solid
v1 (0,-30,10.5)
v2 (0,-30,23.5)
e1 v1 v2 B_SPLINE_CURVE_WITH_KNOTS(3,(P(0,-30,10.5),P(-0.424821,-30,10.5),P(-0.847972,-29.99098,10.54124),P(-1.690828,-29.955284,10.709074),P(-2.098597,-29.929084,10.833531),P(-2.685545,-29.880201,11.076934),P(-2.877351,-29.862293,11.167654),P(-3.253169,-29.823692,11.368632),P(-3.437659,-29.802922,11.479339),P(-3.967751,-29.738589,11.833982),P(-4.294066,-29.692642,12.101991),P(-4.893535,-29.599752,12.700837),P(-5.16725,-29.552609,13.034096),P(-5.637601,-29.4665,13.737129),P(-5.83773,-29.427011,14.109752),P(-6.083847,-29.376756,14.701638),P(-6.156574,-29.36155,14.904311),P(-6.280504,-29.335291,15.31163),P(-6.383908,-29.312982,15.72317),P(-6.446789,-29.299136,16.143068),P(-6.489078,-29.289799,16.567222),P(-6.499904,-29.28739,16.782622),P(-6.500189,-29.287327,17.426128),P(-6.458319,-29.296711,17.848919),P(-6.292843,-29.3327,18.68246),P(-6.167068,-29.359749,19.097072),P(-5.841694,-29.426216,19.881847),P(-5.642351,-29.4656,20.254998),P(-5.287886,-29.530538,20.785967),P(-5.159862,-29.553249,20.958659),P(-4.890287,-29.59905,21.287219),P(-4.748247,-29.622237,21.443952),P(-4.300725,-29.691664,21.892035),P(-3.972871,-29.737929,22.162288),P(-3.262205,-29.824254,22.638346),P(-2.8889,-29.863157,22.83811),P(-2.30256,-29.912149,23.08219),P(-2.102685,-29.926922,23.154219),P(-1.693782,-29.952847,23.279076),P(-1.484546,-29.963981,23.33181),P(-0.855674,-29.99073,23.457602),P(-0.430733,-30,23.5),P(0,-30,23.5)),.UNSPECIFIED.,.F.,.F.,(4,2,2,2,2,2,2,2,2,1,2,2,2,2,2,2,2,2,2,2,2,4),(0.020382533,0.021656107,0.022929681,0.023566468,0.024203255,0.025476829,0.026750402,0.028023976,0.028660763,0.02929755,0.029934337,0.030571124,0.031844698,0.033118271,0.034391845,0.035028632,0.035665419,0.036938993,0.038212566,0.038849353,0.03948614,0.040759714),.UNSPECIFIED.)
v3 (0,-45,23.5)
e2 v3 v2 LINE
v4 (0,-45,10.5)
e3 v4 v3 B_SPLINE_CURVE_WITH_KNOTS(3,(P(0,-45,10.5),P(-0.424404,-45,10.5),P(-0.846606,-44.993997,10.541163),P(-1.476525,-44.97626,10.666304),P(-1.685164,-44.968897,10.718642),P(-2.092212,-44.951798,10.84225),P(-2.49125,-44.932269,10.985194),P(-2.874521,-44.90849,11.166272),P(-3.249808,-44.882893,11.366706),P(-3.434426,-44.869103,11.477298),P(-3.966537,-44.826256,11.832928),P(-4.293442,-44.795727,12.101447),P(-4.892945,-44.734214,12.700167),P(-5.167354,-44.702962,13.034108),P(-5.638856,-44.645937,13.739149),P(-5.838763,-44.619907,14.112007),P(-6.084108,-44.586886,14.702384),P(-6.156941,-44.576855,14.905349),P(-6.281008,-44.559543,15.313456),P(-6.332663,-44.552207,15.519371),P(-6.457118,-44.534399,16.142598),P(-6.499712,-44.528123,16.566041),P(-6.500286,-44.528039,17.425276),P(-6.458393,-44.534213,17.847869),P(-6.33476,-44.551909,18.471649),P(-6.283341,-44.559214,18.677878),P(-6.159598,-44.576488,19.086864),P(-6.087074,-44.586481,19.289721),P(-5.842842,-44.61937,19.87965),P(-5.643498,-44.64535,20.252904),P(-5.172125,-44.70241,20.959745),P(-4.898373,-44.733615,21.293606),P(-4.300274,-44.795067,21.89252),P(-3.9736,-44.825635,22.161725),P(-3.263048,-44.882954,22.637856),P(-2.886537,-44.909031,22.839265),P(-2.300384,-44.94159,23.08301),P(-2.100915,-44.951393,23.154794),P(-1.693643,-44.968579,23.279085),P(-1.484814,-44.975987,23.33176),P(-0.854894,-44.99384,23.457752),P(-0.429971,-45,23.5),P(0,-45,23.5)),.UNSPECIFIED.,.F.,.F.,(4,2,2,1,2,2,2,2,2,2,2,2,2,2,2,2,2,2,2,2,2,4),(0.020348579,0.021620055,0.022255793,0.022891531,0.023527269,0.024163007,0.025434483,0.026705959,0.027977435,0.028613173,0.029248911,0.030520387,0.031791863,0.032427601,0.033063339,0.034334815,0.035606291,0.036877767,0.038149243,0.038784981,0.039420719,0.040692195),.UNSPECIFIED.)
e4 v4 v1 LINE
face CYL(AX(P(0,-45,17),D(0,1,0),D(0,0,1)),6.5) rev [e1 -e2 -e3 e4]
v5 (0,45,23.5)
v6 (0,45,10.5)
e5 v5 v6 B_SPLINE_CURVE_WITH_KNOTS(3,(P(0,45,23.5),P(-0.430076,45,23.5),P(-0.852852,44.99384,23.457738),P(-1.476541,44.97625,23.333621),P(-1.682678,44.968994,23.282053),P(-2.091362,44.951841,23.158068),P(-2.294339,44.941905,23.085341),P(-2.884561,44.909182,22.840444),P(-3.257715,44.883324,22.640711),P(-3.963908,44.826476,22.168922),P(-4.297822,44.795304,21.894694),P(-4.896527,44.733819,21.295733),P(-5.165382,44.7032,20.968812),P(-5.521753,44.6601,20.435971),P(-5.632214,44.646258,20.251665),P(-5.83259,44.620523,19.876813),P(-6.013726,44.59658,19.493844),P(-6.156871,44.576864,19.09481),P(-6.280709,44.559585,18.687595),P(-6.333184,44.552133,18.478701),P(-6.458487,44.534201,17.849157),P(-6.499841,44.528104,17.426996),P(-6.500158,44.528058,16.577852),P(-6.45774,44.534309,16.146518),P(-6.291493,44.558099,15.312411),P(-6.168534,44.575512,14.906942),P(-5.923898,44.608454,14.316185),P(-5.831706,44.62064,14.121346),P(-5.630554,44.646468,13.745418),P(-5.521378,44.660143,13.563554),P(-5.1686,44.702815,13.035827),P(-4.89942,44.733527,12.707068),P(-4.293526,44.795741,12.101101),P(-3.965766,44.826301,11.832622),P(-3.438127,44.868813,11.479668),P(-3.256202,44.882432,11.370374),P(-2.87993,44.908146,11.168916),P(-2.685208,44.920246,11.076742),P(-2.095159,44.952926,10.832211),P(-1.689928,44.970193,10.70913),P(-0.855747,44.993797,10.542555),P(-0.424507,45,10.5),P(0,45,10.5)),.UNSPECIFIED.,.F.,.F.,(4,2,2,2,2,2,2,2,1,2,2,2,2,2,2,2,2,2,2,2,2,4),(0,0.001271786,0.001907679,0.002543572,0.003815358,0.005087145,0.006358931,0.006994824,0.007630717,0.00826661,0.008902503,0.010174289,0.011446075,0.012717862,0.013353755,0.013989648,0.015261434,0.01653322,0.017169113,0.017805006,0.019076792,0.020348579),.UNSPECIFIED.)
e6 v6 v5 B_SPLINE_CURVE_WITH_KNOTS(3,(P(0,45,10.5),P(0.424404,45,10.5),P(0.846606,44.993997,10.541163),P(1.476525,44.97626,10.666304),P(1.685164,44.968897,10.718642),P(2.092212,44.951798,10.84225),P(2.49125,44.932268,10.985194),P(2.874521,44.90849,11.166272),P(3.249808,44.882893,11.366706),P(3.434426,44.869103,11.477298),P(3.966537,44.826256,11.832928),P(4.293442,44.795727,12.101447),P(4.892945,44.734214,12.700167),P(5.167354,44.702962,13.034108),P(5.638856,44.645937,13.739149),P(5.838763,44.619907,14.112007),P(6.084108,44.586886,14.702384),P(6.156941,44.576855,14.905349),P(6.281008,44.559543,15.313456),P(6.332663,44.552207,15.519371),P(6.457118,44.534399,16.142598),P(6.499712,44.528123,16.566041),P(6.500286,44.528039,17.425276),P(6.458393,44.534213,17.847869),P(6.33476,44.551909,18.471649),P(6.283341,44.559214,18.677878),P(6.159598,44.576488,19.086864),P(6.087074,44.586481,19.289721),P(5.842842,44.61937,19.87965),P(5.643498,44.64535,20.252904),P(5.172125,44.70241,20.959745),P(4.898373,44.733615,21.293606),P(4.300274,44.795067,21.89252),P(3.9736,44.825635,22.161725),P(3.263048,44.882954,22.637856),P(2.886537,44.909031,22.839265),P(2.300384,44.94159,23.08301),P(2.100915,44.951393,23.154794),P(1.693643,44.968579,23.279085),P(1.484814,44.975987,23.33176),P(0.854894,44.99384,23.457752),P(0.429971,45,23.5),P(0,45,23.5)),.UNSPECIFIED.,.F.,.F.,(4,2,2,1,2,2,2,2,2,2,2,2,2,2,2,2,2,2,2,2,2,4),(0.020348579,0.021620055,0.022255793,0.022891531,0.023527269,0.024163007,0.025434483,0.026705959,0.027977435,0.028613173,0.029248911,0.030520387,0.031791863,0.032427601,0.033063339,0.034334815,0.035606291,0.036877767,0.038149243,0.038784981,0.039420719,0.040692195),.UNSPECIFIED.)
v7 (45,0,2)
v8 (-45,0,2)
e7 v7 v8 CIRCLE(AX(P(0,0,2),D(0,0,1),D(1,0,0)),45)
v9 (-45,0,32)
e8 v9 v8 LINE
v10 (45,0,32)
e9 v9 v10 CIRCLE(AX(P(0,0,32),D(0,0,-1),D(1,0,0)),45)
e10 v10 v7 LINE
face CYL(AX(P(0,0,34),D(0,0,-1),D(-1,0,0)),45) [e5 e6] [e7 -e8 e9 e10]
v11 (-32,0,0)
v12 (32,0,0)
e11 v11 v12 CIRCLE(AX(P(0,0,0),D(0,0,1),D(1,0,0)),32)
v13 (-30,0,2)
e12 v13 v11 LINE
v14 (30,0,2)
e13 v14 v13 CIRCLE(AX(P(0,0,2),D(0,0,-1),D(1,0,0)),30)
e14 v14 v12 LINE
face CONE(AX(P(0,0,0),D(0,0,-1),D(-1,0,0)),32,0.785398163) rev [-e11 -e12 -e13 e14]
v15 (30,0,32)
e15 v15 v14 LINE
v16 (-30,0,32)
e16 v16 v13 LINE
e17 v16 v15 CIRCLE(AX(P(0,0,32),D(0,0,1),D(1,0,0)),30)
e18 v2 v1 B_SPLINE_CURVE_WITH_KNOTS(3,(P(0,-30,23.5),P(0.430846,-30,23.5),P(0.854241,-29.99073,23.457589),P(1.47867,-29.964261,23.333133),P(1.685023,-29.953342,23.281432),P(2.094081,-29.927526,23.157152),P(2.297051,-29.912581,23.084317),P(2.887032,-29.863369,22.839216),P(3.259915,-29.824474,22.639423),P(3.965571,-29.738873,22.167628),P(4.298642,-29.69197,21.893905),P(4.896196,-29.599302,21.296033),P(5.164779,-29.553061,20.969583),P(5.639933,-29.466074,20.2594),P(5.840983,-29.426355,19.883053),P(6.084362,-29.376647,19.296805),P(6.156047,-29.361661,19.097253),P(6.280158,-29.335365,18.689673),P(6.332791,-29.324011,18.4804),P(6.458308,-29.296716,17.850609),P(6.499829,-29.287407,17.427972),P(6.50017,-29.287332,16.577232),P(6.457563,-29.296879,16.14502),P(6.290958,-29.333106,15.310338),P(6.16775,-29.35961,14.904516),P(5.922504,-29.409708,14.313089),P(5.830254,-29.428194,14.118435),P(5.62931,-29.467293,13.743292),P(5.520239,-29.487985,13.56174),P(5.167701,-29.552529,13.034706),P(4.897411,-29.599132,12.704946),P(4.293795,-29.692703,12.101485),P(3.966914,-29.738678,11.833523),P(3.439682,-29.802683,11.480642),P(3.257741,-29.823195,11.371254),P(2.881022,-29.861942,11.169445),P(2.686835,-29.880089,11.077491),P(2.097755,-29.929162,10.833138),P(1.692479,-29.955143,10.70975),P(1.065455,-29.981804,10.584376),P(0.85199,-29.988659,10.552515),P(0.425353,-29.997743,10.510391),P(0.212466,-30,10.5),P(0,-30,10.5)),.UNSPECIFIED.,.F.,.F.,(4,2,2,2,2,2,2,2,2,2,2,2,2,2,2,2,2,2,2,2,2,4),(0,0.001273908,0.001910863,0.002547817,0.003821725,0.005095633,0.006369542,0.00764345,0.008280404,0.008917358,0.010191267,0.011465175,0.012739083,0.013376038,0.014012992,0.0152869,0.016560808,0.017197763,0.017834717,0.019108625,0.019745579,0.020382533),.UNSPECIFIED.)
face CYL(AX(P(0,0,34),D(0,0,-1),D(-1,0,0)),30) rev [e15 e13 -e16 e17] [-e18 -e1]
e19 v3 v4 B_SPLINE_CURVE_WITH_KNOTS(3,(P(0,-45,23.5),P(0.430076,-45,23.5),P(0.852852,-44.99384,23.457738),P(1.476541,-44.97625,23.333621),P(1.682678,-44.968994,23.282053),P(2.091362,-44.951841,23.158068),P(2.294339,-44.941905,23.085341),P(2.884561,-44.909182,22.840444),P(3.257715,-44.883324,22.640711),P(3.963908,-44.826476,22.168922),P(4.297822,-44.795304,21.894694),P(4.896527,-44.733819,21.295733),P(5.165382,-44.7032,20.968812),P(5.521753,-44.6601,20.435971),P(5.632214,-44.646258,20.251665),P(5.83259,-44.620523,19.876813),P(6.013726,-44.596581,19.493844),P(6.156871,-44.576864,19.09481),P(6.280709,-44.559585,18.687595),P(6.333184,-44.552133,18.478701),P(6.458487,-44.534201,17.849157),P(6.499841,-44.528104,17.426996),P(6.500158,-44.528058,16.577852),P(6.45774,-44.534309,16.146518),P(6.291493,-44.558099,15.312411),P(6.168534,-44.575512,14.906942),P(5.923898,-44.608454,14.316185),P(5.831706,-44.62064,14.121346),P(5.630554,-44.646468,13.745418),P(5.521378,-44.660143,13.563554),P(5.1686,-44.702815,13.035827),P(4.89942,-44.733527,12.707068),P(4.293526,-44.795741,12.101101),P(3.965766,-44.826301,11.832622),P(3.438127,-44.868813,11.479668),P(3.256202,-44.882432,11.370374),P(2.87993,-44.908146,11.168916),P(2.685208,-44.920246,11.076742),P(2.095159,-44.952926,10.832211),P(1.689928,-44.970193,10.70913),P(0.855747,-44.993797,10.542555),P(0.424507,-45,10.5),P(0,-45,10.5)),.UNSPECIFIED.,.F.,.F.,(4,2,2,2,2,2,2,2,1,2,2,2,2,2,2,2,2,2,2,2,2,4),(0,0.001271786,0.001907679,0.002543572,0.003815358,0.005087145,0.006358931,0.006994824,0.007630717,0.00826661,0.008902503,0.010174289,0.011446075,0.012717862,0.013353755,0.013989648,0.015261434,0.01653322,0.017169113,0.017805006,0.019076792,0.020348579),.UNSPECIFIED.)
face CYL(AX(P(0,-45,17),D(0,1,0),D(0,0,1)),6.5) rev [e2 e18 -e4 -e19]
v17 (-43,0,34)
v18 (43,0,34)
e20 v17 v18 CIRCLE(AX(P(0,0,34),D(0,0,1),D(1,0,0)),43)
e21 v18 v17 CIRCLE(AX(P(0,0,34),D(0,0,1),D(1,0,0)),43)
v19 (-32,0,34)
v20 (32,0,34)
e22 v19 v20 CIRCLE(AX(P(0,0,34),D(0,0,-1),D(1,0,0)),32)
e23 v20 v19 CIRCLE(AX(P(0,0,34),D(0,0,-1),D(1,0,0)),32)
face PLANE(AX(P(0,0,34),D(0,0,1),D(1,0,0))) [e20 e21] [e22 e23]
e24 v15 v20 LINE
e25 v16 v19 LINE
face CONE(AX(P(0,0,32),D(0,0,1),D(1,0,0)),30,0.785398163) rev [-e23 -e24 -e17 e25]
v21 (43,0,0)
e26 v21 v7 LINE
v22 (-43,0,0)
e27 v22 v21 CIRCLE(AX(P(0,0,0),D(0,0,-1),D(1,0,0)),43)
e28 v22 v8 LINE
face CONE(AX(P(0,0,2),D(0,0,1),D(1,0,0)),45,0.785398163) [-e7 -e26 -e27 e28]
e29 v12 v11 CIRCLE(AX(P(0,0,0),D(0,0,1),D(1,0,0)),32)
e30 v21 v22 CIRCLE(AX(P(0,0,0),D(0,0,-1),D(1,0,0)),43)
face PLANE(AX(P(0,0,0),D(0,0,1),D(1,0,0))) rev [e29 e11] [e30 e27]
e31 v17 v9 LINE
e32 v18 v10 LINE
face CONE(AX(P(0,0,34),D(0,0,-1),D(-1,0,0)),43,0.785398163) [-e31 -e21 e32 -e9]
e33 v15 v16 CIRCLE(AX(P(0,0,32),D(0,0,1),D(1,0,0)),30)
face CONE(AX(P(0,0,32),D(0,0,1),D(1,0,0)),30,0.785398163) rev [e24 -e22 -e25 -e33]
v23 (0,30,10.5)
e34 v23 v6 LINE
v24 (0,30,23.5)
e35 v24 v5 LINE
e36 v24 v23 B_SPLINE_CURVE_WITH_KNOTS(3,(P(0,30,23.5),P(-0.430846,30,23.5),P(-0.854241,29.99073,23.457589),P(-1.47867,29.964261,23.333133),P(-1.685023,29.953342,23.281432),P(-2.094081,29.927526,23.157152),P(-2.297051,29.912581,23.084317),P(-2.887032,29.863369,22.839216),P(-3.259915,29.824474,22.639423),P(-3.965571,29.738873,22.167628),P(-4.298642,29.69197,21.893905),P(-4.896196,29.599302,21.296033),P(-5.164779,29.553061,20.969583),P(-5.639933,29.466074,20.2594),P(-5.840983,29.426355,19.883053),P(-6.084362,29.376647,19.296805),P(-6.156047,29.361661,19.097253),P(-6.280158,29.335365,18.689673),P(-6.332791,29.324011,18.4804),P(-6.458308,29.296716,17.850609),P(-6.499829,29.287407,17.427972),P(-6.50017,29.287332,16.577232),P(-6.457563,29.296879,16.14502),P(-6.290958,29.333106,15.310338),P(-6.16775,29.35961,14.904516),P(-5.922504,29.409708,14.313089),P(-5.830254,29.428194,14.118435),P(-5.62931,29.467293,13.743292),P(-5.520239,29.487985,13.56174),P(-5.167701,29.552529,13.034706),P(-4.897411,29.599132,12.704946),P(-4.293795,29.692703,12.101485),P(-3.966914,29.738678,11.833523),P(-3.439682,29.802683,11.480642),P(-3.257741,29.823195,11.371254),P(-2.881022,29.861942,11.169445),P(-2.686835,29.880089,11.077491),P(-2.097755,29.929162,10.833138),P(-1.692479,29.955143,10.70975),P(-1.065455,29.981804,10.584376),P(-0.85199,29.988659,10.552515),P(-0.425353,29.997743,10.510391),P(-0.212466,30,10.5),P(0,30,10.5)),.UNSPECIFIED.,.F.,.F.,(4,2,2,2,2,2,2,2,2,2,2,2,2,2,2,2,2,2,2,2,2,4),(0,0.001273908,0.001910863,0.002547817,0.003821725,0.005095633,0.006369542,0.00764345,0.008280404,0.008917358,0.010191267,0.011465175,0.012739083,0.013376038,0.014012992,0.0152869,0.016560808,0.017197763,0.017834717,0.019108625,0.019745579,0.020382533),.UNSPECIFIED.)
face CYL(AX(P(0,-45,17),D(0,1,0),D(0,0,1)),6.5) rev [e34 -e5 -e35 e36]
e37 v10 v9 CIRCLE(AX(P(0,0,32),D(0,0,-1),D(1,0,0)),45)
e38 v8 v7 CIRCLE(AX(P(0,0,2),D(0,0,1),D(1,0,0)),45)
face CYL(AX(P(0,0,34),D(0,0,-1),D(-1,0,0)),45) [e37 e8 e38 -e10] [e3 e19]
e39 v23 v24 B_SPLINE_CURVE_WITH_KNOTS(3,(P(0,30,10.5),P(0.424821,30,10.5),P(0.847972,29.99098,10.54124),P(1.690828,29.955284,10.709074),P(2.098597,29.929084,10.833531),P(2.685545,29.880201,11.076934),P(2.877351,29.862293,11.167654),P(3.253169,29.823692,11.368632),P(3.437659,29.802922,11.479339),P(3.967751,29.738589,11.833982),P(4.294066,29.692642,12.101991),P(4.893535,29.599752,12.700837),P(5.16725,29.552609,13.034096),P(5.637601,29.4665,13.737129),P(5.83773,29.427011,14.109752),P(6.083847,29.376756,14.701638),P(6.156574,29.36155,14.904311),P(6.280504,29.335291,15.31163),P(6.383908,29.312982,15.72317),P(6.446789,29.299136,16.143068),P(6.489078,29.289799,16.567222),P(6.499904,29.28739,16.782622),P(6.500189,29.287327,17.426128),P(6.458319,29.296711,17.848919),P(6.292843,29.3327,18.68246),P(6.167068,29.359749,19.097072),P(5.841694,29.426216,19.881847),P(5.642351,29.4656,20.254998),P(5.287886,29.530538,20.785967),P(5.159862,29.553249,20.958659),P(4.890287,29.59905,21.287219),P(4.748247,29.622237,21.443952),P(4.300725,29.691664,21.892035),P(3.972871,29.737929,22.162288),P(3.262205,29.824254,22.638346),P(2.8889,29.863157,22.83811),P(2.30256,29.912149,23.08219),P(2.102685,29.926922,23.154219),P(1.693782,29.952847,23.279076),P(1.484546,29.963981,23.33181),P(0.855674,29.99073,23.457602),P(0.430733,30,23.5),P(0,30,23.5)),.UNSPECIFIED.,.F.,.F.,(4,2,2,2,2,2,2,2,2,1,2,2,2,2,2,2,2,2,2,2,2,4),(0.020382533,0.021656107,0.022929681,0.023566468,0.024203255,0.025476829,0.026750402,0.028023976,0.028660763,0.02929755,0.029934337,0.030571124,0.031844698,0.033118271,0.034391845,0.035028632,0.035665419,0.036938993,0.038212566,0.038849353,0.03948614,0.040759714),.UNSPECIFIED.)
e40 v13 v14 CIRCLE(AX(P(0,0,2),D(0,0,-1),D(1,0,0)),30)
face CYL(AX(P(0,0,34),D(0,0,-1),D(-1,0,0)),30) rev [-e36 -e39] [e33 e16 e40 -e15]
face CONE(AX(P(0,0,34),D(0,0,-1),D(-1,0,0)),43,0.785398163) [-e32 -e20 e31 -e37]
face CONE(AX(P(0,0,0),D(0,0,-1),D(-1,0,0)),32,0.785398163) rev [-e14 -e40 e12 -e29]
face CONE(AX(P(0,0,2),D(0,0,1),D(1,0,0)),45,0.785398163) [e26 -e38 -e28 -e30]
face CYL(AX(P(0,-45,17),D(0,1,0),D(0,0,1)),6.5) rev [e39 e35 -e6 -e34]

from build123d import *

# Parameters (mm, degrees)
SKETCH1_R               = 45
SKETCH1_R_2             = 30
BOSS_EXTRUDE1_DEPTH     = 34
CUT_EXTRUDE1_DEPTH      = 73.15261603
CUT_EXTRUDE1_DEPTH_BACK = 73.15261603
SKETCH2_R               = 6.5
CHAMFER1_SIZE           = 2


with BuildPart() as part:
    # Sketch1 → Boss-Extrude1 (new body)
    with BuildSketch(Plane.XY):
        Circle(SKETCH1_R)
        Circle(SKETCH1_R_2, mode=Mode.SUBTRACT)
    extrude(amount=BOSS_EXTRUDE1_DEPTH)

    # Sketch2 → Cut-Extrude1 (cut, two sides: drawn at the far end of the back side and taken through both)
    with BuildSketch(Plane(origin=(0, 0, 0), x_dir=(1, 0, 0), z_dir=(0, 1, 0)).offset(-CUT_EXTRUDE1_DEPTH_BACK)):
        with Locations(Location((0, -17, 0), (0, 0, 270))):
            Circle(SKETCH2_R)
    extrude(amount=CUT_EXTRUDE1_DEPTH + CUT_EXTRUDE1_DEPTH_BACK, mode=Mode.SUBTRACT)

    # Chamfer1
    chamfer1_edges = [part.edges().sort_by_distance(p)[0] for p in [
        (-45, 0, 0),
        (-45, 0, 34),
        (-30, 0, 0),
        (-30, 0, 34),
    ]]
    chamfer(chamfer1_edges, length=CHAMFER1_SIZE)


solid = part.part
